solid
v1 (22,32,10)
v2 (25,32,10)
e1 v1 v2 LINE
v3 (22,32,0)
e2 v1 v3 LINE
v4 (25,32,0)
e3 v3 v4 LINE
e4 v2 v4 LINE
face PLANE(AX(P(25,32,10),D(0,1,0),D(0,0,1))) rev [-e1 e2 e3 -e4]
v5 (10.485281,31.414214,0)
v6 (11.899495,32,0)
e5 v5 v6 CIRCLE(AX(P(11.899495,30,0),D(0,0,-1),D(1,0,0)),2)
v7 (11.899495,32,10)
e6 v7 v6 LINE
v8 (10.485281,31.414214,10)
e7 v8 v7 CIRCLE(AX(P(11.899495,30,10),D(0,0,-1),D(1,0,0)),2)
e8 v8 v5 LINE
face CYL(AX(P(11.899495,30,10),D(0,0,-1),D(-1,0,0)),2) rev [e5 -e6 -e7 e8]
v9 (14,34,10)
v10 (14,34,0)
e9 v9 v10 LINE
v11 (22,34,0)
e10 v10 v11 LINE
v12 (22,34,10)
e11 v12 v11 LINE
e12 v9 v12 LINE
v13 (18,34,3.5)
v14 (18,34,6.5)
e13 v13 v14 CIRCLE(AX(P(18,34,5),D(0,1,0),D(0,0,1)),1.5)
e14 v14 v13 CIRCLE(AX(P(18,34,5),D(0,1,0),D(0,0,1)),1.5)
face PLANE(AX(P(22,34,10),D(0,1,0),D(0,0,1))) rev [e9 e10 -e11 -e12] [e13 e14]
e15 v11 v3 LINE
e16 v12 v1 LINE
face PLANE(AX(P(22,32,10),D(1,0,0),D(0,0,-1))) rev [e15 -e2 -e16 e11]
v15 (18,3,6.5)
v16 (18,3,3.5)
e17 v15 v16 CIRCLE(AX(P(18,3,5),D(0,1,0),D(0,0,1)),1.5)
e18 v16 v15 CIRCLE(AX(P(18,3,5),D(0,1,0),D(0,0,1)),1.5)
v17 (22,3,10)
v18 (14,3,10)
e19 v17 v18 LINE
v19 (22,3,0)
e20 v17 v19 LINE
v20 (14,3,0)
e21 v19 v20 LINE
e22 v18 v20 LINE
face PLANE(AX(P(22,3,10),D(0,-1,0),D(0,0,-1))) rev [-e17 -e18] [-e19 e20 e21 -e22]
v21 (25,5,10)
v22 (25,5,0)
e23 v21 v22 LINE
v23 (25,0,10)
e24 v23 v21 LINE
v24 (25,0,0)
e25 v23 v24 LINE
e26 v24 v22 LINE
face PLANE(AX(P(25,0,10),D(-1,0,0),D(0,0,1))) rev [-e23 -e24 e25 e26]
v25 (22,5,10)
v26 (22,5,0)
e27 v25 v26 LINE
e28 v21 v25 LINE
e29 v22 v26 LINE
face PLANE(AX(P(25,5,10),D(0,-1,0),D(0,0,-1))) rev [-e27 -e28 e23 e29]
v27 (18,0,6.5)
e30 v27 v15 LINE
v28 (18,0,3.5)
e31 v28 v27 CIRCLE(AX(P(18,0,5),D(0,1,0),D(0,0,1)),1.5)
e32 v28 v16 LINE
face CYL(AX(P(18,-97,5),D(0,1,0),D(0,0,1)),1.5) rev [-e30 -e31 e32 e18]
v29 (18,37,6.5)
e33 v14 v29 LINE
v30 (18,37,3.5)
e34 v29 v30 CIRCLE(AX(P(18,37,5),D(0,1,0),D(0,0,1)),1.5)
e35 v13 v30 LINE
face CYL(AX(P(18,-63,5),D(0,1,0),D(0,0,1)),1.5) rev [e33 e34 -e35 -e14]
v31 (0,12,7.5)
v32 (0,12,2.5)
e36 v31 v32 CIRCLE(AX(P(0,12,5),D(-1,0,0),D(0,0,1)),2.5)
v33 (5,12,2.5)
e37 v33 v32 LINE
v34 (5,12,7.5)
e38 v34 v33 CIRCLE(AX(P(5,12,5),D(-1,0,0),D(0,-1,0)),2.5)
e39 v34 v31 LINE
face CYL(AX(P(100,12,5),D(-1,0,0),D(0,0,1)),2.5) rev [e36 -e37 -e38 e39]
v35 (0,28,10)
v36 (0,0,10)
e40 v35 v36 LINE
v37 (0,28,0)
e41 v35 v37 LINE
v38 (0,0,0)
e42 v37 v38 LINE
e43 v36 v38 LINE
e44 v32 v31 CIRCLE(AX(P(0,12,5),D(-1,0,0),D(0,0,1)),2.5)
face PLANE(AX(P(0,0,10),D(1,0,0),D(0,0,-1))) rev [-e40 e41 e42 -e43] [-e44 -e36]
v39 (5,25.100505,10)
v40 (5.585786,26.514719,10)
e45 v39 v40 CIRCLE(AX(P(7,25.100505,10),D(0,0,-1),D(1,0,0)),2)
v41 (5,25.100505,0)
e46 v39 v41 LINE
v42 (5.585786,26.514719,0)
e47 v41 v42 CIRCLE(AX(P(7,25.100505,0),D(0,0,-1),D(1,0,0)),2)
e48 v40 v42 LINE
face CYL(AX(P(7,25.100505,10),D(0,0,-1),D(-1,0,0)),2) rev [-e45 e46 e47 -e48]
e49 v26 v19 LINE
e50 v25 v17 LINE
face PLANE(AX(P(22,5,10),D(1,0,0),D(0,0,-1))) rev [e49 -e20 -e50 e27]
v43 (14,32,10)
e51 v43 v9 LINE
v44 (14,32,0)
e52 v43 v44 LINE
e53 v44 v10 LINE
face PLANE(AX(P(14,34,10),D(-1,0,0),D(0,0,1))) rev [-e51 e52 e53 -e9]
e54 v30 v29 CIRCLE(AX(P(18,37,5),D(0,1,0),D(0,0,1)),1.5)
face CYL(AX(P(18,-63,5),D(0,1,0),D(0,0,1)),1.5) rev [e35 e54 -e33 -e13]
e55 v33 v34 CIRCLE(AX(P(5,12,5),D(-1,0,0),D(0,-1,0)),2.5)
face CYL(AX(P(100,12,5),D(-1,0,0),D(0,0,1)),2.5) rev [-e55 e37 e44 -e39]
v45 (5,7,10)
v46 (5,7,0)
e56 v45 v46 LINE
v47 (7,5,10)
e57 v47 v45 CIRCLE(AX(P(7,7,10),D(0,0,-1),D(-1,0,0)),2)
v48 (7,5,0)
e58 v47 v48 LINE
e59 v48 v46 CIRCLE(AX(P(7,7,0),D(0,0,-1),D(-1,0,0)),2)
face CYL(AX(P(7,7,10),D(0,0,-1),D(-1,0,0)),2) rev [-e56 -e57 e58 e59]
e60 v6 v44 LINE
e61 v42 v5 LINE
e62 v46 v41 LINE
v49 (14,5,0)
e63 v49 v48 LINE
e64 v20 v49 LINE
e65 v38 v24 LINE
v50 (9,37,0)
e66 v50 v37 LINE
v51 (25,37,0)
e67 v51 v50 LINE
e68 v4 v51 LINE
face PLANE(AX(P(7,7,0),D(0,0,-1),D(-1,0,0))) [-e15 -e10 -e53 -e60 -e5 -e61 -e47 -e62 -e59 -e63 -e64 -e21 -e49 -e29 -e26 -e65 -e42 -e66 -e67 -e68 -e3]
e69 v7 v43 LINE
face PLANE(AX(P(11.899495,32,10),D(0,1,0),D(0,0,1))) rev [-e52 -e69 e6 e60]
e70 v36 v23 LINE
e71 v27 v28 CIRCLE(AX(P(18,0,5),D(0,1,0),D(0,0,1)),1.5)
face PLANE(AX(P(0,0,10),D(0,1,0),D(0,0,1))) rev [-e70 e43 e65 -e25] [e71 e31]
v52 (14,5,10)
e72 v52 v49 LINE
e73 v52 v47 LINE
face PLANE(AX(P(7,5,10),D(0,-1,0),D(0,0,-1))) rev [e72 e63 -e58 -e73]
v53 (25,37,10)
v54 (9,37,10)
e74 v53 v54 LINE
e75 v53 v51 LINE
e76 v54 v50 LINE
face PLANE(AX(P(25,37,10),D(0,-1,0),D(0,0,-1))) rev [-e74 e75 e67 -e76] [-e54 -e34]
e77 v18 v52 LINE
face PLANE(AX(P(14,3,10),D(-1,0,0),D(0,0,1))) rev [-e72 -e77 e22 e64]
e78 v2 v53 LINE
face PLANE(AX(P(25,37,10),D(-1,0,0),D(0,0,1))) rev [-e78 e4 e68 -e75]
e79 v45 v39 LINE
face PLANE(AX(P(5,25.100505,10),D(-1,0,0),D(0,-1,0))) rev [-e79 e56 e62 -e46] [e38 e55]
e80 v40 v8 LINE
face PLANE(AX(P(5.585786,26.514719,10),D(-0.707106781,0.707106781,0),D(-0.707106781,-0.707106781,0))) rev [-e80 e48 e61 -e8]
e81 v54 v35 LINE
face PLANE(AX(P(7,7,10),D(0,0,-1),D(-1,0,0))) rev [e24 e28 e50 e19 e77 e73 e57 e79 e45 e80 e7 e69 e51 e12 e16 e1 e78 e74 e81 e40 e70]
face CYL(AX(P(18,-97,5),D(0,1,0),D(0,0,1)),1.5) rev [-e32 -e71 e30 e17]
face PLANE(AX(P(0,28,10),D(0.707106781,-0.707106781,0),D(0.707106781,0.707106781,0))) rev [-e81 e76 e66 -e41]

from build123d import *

# Parameters (mm, degrees)
C_CLIP_BODY_DEPTH      = 10
FLANGE_HOLE_1_SKETCH_R = 1.5
FLANGE_HOLE_1_3_DEPTH  = 100
FLANGE_HOLE_2_SKETCH_R = 1.5
FLANGE_HOLE_2_3_DEPTH  = 100
WEB_HOLE_SKETCH_R      = 2.5
WEB_HOLE_5_DEPTH       = 100


with BuildPart() as part:
    # C Clip Profile Sketch → C Clip Body (new body)
    with BuildSketch(Plane.XY):
        with BuildLine():
            Line((0, 0), (0, 28))
            Line((0, 28), (9, 37))
            Line((9, 37), (25, 37))
            Line((25, 37), (25, 32))
            Line((25, 32), (22, 32))
            Line((22, 32), (22, 34))
            Line((22, 34), (14, 34))
            Line((14, 34), (14, 32))
            Line((14, 32), (11.899494937, 32))
            ThreePointArc((11.899494937, 32), (11.134128072, 31.847759065), (10.485281374, 31.414213562))
            Line((10.485281374, 31.414213562), (5.585786438, 26.514718626))
            ThreePointArc((5.585786438, 26.514718626), (5.152240935, 25.865871928), (5, 25.100505063))
            Line((5, 25.100505063), (5, 7))
            ThreePointArc((5, 7), (5.585786438, 5.585786438), (7, 5))
            Line((7, 5), (14, 5))
            Line((14, 5), (14, 3))
            Line((14, 3), (22, 3))
            Line((22, 3), (22, 5))
            Line((22, 5), (25, 5))
            Line((25, 5), (25, 0))
            Line((25, 0), (0, 0))
        make_face()
    extrude(amount=C_CLIP_BODY_DEPTH)

    # Flange Hole 1 Sketch → Flange Hole 1 Ø3 (cut)
    with BuildSketch(Plane(origin=(0, 3, 0), x_dir=(1, 0, 0), z_dir=(0, 1, 0))):
        with Locations(Location((18, -5, 0), (0, 0, 270))):
            Circle(FLANGE_HOLE_1_SKETCH_R)
    extrude(amount=-FLANGE_HOLE_1_3_DEPTH, mode=Mode.SUBTRACT)

    # Flange Hole 2 Sketch → Flange Hole 2 Ø3 (cut)
    with BuildSketch(Plane(origin=(0, 37, 0), x_dir=(1, 0, 0), z_dir=(0, 1, 0))):
        with Locations(Location((18, -5, 0), (0, 0, 270))):
            Circle(FLANGE_HOLE_2_SKETCH_R)
    extrude(amount=-FLANGE_HOLE_2_3_DEPTH, mode=Mode.SUBTRACT)

    # Web Hole Sketch → Web Hole Ø5 (cut)
    with BuildSketch(Plane.ZY):
        with Locations((5, 12)):
            Circle(WEB_HOLE_SKETCH_R)
    extrude(amount=-WEB_HOLE_5_DEPTH, mode=Mode.SUBTRACT)


solid = part.part
